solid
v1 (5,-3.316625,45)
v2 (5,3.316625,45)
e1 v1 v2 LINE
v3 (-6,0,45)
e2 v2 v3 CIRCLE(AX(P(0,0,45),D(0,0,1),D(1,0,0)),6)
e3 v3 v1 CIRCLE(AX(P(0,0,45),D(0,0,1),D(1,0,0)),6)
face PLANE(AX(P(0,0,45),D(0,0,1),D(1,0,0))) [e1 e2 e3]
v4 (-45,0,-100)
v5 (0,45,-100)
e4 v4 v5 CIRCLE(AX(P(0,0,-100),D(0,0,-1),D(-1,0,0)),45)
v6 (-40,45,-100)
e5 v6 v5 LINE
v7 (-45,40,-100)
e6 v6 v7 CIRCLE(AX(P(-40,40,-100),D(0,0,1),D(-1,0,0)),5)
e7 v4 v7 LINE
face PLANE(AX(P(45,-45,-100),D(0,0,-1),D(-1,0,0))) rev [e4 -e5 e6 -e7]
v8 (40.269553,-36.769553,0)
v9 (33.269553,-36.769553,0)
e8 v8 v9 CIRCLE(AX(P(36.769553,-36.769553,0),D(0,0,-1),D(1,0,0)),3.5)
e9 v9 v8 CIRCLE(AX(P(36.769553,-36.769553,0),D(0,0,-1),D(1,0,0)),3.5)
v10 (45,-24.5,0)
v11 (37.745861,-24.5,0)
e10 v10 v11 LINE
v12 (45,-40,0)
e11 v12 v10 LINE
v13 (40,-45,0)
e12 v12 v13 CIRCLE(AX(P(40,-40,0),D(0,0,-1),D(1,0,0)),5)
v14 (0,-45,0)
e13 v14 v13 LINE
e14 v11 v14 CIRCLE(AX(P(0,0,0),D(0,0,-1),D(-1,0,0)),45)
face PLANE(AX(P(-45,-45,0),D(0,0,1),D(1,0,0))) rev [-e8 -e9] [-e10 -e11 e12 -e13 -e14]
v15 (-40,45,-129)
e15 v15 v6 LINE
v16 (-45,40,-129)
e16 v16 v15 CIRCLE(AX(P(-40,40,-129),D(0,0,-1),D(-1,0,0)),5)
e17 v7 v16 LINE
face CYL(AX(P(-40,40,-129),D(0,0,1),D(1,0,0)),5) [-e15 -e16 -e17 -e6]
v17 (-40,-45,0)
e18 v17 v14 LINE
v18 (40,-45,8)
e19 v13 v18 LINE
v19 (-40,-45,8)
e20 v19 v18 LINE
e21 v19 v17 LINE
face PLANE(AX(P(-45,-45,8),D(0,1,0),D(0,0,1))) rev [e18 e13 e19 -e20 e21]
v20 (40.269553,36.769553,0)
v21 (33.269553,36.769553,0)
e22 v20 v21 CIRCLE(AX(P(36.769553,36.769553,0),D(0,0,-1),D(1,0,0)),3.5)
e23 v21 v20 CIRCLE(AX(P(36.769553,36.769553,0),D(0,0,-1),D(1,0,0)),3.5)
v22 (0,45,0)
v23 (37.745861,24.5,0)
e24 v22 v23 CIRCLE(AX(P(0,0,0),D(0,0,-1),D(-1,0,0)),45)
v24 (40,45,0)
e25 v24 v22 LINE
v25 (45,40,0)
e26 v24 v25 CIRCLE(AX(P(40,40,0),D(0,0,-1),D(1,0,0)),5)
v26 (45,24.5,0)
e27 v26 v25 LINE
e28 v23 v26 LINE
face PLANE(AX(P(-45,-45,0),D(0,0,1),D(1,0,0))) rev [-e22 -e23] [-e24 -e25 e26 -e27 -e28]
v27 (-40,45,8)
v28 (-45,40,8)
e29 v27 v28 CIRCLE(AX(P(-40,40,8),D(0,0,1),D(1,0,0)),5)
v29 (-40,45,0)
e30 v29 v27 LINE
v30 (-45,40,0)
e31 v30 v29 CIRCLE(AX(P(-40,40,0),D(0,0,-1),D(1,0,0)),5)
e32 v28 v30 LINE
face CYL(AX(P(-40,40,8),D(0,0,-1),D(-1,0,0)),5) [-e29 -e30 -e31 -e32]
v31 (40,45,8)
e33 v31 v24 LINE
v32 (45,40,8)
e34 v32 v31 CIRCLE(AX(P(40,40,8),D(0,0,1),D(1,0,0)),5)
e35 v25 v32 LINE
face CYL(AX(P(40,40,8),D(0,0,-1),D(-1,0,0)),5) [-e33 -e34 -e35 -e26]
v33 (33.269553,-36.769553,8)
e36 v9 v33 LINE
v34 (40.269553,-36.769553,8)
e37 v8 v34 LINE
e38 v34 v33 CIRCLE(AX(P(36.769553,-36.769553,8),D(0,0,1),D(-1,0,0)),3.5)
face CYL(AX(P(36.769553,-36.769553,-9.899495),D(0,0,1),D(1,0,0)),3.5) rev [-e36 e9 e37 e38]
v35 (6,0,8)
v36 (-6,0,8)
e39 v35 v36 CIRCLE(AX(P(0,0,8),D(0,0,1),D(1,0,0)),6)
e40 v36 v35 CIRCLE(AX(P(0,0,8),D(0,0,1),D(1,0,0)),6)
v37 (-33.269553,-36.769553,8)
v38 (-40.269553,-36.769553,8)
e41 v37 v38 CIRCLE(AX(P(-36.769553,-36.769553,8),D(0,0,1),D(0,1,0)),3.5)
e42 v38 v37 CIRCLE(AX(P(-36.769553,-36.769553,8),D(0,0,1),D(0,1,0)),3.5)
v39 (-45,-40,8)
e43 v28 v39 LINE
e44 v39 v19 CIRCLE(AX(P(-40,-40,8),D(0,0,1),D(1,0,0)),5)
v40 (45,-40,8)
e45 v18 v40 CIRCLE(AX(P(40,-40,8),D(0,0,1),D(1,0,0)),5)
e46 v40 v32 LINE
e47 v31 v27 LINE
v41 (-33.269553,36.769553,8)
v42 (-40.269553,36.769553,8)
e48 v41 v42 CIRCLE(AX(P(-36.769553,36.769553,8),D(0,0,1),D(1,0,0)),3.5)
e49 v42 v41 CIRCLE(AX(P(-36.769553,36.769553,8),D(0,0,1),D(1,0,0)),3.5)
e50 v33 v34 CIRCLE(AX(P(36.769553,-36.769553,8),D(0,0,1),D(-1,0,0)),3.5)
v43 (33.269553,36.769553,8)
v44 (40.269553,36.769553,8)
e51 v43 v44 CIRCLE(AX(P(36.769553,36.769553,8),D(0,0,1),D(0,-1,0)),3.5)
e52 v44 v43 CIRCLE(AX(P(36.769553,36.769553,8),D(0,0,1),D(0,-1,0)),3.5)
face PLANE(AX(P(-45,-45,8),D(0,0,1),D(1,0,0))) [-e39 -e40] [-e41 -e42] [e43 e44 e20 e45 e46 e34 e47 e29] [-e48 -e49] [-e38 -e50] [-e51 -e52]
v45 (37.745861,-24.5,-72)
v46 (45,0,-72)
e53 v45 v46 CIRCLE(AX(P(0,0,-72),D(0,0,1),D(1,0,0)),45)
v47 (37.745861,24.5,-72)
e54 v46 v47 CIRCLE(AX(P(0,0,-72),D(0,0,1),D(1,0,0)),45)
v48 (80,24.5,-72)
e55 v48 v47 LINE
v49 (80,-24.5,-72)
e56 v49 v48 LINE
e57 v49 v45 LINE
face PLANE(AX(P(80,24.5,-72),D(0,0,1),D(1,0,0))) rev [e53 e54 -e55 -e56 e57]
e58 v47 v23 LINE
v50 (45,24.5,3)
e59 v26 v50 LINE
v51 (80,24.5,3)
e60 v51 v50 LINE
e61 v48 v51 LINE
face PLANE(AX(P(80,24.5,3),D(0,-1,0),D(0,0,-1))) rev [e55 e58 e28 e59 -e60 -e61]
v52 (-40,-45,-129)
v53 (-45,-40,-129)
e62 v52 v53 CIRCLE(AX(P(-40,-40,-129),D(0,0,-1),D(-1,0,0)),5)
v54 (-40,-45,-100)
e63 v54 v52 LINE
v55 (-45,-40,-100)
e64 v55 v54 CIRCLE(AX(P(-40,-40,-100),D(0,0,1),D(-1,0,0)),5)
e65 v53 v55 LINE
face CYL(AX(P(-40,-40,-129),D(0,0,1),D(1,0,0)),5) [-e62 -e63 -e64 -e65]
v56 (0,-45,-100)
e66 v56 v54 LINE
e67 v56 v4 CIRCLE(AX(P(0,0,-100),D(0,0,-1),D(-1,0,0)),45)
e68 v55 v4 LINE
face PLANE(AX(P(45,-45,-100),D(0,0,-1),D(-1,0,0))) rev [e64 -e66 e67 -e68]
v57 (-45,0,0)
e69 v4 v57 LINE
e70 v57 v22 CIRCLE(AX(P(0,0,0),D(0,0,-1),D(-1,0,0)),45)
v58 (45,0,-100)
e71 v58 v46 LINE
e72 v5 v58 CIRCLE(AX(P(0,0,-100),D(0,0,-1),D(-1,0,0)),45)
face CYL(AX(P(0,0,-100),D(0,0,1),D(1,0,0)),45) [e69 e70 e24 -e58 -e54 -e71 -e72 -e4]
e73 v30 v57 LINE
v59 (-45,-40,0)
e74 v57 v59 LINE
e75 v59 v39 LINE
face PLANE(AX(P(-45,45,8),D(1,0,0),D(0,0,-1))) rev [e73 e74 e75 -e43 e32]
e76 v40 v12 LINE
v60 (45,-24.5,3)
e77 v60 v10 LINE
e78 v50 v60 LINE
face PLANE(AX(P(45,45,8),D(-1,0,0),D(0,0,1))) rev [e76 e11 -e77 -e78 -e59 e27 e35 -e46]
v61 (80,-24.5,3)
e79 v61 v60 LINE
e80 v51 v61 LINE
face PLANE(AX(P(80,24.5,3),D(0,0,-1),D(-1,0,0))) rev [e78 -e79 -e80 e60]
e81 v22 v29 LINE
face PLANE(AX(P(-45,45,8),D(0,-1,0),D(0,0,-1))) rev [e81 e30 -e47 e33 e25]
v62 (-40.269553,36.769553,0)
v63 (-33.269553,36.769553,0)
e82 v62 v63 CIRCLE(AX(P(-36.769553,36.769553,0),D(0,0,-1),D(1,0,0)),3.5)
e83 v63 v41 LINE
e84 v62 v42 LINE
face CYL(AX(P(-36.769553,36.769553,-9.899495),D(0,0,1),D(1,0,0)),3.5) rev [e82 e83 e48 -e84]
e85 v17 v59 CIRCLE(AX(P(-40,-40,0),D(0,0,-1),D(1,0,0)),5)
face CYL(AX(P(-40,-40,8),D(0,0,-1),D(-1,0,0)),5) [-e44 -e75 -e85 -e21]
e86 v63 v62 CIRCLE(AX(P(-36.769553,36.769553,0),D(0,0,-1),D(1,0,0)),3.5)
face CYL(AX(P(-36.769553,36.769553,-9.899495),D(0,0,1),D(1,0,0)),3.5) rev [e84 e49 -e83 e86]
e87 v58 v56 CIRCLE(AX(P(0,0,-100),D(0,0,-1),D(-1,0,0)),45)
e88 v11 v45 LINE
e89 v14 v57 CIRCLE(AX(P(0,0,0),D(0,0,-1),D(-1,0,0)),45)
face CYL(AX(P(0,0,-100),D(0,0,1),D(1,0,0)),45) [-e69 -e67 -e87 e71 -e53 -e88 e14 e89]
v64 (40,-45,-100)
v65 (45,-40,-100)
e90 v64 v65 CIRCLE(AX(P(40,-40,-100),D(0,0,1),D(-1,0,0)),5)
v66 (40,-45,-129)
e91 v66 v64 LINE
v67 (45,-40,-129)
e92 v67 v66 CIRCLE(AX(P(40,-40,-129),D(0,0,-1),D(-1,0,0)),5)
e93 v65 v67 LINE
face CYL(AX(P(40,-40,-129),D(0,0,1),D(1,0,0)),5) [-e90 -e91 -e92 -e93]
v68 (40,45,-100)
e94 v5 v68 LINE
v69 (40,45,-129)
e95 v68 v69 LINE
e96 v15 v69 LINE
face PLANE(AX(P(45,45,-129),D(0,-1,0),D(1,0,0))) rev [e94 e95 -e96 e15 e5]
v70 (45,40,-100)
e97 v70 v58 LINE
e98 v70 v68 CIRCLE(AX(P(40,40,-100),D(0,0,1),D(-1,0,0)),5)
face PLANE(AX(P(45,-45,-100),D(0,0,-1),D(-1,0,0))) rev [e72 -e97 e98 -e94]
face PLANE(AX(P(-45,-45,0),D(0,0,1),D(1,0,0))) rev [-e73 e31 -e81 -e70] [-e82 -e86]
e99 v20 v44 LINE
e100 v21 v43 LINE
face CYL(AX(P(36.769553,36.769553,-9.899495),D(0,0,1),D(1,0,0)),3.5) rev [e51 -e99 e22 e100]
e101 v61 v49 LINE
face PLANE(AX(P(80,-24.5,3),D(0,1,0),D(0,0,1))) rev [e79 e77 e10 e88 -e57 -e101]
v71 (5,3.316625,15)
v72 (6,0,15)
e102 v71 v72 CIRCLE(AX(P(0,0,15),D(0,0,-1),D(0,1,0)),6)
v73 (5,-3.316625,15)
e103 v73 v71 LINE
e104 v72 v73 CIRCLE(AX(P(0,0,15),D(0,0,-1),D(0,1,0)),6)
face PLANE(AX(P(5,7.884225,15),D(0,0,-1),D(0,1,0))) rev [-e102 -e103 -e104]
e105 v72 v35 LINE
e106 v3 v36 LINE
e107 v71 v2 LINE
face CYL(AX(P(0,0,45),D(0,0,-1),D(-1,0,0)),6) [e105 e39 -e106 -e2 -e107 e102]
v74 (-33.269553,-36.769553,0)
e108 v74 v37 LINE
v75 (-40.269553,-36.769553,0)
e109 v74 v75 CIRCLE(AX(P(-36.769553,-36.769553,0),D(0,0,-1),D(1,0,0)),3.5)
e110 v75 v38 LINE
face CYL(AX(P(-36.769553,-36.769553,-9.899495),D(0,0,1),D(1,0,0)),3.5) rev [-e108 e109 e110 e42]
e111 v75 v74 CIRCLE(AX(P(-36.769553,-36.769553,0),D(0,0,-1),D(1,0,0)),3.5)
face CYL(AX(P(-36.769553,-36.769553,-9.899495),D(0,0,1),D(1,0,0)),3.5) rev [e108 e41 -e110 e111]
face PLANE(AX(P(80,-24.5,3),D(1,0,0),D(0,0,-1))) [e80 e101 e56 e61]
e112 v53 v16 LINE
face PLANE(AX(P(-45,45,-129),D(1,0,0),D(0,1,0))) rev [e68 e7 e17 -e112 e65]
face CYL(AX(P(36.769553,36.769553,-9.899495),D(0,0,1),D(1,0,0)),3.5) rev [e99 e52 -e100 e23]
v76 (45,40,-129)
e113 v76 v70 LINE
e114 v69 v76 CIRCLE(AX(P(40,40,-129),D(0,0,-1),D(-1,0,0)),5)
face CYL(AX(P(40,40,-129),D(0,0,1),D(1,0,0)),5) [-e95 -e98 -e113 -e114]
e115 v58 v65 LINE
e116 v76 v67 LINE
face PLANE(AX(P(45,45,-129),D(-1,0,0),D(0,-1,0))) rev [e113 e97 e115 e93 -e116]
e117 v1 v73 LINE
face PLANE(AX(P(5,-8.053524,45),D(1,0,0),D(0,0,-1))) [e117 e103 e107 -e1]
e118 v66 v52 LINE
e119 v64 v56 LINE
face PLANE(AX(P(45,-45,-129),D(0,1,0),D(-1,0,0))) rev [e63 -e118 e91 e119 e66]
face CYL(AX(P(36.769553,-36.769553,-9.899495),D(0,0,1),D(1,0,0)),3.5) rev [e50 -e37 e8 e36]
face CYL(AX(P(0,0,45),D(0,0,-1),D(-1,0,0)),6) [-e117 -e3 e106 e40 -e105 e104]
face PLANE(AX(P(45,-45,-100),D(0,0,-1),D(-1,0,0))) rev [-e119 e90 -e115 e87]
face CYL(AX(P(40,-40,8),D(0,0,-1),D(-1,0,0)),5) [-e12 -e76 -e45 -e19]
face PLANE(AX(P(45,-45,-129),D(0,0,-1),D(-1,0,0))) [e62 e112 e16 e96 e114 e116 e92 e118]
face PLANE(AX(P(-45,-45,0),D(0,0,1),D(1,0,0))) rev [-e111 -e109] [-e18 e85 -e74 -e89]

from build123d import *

# Parameters (mm, degrees)
SKETCH_1_W               = 90
SKETCH_1_H               = 90
EXTRUDE_1_DEPTH          = 8
SKETCH_2_R               = 45
EXTRUDE_2_DEPTH          = 100
SKETCH_3_W               = 90
SKETCH_3_H               = 90
EXTRUDE_3_DEPTH          = 29
SKETCH_4_R               = 6
EXTRUDE_4_DEPTH          = 37
SKETCH_6_W               = 75
SKETCH_6_H               = 49
EXTRUDE_5_DEPTH          = 80
SKETCH_7_R               = 3.5
CUT_EXTRUDE_1_DEPTH      = 8
FILLET_1_R               = 5
FILLET_2_R               = 5
SKETCH_9_W               = 30
SKETCH_9_H               = 15.937749453
CUT_EXTRUDE_2_DEPTH      = 1
PATTERN_CIRCULAR_1_COUNT = 4


with BuildPart() as part:
    # 草图1 → 凸台-拉伸1 (new body)
    with BuildSketch(Plane.XY):
        Rectangle(SKETCH_1_W, SKETCH_1_H)
    extrude(amount=EXTRUDE_1_DEPTH)

    # 草图2 → 凸台-拉伸2 (add)
    with BuildSketch(Plane(origin=(0, 0, 0), x_dir=(-1, 0, 0), z_dir=(0, 0, -1))):
        Circle(SKETCH_2_R)
    extrude(amount=EXTRUDE_2_DEPTH)

    # 草图3 → 凸台-拉伸3 (add)
    with BuildSketch(Plane(origin=(0, 0, -100), x_dir=(-1, 0, 0), z_dir=(0, 0, -1))):
        Rectangle(SKETCH_3_W, SKETCH_3_H)
    extrude(amount=EXTRUDE_3_DEPTH)

    # 草图4 → 凸台-拉伸4 (add)
    with BuildSketch(Plane.XY.offset(8)):
        Circle(SKETCH_4_R)
    extrude(amount=EXTRUDE_4_DEPTH)

    # 草图6 → 凸台-拉伸5 (add)
    with BuildSketch(Plane(origin=(0, 0, 0), x_dir=(0, 0, -1), z_dir=(1, 0, 0))):
        with Locations((34.5, 0)):
            Rectangle(SKETCH_6_W, SKETCH_6_H)
    extrude(amount=EXTRUDE_5_DEPTH)

    # 草图7 → 切除-拉伸1 (cut)
    with BuildSketch(Plane.XY.offset(8)):
        with Locations((-36.769552622, 36.769552622)):
            Circle(SKETCH_7_R)
    cut_extrude_1 = extrude(amount=-CUT_EXTRUDE_1_DEPTH, mode=Mode.SUBTRACT)

    # 圆角1
    fillet_1_edges = [part.edges().sort_by_distance(p)[0] for p in [
        (-45, 45, 4),
        (45, 45, 4),
        (45, -45, 4),
        (-45, -45, 4),
    ]]
    fillet(fillet_1_edges, radius=FILLET_1_R)

    # 圆角2
    fillet_2_edges = [part.edges().sort_by_distance(p)[0] for p in [
        (45, 45, -114.5),
        (45, -45, -114.5),
        (-45, -45, -114.5),
        (-45, 45, -114.5),
    ]]
    fillet(fillet_2_edges, radius=FILLET_2_R)

    # 草图9 → 切除-拉伸2 (cut)
    with BuildSketch(Plane(origin=(6, 0, 0), x_dir=(0, 0, -1), z_dir=(1, 0, 0))):
        with Locations((-30, -0.084649365)):
            Rectangle(SKETCH_9_W, SKETCH_9_H)
    extrude(amount=-CUT_EXTRUDE_2_DEPTH, mode=Mode.SUBTRACT)

    # 阵列(圆周)1: 切除-拉伸1 ×4 about axis
    pattern_circular_1_axis = Axis((0, 0, 0), (0, 0, 1))
    for i in range(1, PATTERN_CIRCULAR_1_COUNT):
        add(cut_extrude_1.rotate(pattern_circular_1_axis, i * 360 / PATTERN_CIRCULAR_1_COUNT), mode=Mode.SUBTRACT)


solid = part.part
